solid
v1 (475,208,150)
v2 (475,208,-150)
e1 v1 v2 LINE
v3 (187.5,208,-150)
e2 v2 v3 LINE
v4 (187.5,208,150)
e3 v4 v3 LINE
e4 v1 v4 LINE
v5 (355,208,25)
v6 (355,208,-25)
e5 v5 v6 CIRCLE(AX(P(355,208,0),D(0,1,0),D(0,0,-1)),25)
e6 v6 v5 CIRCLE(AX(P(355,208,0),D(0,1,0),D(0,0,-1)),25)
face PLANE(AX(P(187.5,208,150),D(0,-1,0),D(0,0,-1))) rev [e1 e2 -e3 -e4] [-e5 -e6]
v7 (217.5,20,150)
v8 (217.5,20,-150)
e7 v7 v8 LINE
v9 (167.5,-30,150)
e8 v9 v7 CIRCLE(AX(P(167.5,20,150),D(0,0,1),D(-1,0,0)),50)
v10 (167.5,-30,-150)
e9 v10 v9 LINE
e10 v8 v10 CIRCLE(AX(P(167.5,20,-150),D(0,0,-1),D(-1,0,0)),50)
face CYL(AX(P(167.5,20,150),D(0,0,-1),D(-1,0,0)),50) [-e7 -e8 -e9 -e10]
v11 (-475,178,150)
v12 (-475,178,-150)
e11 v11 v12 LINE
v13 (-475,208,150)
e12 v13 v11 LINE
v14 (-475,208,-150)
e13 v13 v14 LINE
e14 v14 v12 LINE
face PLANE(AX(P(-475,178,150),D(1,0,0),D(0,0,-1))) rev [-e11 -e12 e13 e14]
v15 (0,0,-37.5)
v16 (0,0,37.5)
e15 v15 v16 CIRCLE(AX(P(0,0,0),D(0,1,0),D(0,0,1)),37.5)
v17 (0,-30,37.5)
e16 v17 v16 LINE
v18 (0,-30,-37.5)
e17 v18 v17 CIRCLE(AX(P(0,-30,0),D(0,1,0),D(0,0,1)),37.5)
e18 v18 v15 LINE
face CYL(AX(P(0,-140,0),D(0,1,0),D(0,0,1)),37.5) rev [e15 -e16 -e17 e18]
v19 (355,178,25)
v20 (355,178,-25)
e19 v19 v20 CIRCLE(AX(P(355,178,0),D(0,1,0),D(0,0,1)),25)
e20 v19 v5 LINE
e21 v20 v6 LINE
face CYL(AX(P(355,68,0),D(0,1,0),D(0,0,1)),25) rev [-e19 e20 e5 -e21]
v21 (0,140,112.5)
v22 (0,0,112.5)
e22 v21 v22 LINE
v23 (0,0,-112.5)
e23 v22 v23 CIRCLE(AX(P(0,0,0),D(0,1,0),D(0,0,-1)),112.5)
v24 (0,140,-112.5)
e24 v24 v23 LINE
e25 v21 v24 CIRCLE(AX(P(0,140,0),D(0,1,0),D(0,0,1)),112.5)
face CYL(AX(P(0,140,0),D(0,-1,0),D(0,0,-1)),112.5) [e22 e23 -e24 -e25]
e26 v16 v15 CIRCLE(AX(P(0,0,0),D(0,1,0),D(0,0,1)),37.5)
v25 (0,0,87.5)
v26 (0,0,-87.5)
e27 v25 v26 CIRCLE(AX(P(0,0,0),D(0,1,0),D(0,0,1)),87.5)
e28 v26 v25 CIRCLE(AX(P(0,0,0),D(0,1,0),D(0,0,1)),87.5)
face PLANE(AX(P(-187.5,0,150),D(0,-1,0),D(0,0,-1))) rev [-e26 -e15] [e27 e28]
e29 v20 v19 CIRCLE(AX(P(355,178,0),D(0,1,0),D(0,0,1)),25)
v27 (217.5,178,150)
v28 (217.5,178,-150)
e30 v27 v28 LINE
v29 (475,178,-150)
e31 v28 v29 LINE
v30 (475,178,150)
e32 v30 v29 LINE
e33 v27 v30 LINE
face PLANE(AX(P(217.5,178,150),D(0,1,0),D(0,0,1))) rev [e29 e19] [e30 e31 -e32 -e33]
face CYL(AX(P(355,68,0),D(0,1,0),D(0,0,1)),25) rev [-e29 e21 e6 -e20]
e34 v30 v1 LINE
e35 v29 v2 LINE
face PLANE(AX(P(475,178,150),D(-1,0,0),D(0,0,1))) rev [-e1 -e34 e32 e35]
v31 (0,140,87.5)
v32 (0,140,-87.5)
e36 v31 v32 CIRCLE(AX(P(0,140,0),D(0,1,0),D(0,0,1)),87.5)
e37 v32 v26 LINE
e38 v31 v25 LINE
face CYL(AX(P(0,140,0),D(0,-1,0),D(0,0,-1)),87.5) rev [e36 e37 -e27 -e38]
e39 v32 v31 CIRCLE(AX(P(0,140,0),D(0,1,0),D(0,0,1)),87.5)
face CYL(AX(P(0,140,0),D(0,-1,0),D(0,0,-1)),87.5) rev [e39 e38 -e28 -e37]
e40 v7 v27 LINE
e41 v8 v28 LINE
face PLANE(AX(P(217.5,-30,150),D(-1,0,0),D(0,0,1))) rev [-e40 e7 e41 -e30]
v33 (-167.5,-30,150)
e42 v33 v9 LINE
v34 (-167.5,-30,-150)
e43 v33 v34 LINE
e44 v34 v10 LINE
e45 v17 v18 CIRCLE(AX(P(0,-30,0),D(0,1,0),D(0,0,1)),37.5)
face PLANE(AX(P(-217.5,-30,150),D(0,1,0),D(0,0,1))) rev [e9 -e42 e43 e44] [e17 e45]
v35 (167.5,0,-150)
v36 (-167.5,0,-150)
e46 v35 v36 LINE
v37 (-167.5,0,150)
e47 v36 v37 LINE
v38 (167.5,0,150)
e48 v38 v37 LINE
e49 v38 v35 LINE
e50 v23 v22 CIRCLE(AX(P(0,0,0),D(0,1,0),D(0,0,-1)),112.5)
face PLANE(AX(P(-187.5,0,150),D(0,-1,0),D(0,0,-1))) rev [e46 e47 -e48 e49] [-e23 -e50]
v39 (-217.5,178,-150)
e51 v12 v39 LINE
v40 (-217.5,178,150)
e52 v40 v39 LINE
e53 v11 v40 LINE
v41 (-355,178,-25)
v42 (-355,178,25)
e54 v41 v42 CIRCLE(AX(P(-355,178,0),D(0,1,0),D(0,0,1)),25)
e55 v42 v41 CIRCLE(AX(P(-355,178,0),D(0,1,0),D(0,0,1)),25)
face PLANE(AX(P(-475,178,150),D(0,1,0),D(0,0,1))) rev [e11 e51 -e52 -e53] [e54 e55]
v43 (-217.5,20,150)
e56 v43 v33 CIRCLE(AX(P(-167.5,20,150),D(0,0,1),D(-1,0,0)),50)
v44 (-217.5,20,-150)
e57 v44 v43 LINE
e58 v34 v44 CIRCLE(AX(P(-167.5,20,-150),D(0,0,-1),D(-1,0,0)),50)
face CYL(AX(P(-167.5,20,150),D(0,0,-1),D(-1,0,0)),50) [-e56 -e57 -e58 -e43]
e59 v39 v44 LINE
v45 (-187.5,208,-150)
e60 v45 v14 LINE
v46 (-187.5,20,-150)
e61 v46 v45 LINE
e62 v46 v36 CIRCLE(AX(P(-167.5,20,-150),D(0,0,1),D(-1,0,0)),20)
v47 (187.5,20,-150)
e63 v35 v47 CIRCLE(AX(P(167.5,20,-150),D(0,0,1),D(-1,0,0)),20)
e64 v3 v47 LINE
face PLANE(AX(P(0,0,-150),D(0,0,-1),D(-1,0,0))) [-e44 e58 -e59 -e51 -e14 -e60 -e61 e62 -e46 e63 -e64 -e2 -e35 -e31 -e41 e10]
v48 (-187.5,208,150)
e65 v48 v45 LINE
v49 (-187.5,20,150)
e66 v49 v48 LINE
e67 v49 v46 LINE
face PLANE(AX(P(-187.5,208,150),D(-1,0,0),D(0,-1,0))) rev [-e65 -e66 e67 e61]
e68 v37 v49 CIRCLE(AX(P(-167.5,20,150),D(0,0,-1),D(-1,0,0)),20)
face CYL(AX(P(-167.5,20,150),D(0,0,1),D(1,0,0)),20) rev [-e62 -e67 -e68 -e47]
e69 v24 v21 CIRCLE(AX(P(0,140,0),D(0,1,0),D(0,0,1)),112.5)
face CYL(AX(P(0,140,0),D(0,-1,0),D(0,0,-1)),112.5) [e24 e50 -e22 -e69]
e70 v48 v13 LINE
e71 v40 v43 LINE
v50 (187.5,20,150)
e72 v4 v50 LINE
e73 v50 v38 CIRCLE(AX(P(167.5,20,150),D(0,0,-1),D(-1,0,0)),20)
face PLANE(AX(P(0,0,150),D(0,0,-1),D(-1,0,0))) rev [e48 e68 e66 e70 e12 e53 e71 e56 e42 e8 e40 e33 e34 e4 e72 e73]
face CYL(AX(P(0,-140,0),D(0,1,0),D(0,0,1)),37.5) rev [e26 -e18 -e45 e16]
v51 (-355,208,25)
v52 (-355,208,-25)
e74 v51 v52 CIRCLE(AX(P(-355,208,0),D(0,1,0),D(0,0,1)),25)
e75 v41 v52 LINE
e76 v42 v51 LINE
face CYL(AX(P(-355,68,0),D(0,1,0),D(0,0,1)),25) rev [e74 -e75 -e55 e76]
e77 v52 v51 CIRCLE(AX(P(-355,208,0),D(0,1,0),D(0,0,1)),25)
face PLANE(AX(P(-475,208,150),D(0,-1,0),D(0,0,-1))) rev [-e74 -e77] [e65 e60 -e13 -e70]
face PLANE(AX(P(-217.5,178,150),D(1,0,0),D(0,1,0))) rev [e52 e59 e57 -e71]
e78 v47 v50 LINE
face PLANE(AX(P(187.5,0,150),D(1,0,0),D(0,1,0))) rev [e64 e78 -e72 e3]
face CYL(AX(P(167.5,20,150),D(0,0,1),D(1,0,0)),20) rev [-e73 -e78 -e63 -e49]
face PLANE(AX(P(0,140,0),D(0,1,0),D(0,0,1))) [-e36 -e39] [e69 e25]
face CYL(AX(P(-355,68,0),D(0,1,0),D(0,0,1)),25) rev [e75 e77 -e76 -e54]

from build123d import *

# Parameters (mm, degrees)
Z_BRACKET_BODY_DEPTH        = 150
TUBE_BOSS_SKETCH_R          = 112.5
TUBE_BOSS_SKETCH_R_2        = 87.5
TUBE_BOSS_225X_175_DEPTH    = 140
CENTRE_HOLE_SKETCH_R        = 37.5
CENTRE_HOLE_75_DEPTH        = 140
FLANGE_HOLES_SKETCH_R       = 25
FLANGE_MOUNTING_HOLES_DEPTH = 140
BEND_FILLET_R20_R           = 20
BEND_FILLET_R50_R           = 50


with BuildPart() as part:
    # Bracket Profile Sketch → Z Bracket Body (new, symmetric)
    with BuildSketch(Plane.XY):
        Polygon((-475, 208), (-187.5, 208), (-187.5, 0), (187.5, 0), (187.5, 208), (475, 208), (475, 178), (217.5, 178), (217.5, -30), (-217.5, -30), (-217.5, 178), (-475, 178), align=None)
    extrude(amount=Z_BRACKET_BODY_DEPTH, both=True)

    # Tube Boss Sketch → Tube Boss Ø225xØ175 (add)
    with BuildSketch(Plane(origin=(0, 0, 0), x_dir=(1, 0, 0), z_dir=(0, 1, 0))):
        with Locations(Location((0, 0, 0), (0, 0, 90))):
            Circle(TUBE_BOSS_SKETCH_R)
        with Locations(Location((0, 0, 0), (0, 0, 270))):
            Circle(TUBE_BOSS_SKETCH_R_2, mode=Mode.SUBTRACT)
    extrude(amount=TUBE_BOSS_225X_175_DEPTH)

    # Centre Hole Sketch → Centre Hole Ø75 (cut)
    with BuildSketch(Plane(origin=(0, 0, 0), x_dir=(1, 0, 0), z_dir=(0, 1, 0))):
        with Locations(Location((0, 0, 0), (0, 0, 270))):
            Circle(CENTRE_HOLE_SKETCH_R)
    extrude(amount=-CENTRE_HOLE_75_DEPTH, mode=Mode.SUBTRACT)

    # Flange Holes Sketch → Flange Mounting Holes (cut)
    with BuildSketch(Plane(origin=(0, 208, 0), x_dir=(1, 0, 0), z_dir=(0, 1, 0))):
        with Locations(Location((-355, 0, 0), (0, 0, 270))):
            Circle(FLANGE_HOLES_SKETCH_R)
        with Locations(Location((355, 0, 0), (0, 0, 270))):
            Circle(FLANGE_HOLES_SKETCH_R)
    extrude(amount=-FLANGE_MOUNTING_HOLES_DEPTH, mode=Mode.SUBTRACT)

    # Bend Fillet R20
    bend_fillet_r20_edges = [part.edges().sort_by_distance(p)[0] for p in [
        (-187.5, 0, 0),
        (187.5, 0, 0),
    ]]
    fillet(bend_fillet_r20_edges, radius=BEND_FILLET_R20_R)

    # Bend Fillet R50
    bend_fillet_r50_edges = [part.edges().sort_by_distance(p)[0] for p in [
        (217.5, -30, 0),
        (-217.5, -30, 0),
    ]]
    fillet(bend_fillet_r50_edges, radius=BEND_FILLET_R50_R)


solid = part.part
